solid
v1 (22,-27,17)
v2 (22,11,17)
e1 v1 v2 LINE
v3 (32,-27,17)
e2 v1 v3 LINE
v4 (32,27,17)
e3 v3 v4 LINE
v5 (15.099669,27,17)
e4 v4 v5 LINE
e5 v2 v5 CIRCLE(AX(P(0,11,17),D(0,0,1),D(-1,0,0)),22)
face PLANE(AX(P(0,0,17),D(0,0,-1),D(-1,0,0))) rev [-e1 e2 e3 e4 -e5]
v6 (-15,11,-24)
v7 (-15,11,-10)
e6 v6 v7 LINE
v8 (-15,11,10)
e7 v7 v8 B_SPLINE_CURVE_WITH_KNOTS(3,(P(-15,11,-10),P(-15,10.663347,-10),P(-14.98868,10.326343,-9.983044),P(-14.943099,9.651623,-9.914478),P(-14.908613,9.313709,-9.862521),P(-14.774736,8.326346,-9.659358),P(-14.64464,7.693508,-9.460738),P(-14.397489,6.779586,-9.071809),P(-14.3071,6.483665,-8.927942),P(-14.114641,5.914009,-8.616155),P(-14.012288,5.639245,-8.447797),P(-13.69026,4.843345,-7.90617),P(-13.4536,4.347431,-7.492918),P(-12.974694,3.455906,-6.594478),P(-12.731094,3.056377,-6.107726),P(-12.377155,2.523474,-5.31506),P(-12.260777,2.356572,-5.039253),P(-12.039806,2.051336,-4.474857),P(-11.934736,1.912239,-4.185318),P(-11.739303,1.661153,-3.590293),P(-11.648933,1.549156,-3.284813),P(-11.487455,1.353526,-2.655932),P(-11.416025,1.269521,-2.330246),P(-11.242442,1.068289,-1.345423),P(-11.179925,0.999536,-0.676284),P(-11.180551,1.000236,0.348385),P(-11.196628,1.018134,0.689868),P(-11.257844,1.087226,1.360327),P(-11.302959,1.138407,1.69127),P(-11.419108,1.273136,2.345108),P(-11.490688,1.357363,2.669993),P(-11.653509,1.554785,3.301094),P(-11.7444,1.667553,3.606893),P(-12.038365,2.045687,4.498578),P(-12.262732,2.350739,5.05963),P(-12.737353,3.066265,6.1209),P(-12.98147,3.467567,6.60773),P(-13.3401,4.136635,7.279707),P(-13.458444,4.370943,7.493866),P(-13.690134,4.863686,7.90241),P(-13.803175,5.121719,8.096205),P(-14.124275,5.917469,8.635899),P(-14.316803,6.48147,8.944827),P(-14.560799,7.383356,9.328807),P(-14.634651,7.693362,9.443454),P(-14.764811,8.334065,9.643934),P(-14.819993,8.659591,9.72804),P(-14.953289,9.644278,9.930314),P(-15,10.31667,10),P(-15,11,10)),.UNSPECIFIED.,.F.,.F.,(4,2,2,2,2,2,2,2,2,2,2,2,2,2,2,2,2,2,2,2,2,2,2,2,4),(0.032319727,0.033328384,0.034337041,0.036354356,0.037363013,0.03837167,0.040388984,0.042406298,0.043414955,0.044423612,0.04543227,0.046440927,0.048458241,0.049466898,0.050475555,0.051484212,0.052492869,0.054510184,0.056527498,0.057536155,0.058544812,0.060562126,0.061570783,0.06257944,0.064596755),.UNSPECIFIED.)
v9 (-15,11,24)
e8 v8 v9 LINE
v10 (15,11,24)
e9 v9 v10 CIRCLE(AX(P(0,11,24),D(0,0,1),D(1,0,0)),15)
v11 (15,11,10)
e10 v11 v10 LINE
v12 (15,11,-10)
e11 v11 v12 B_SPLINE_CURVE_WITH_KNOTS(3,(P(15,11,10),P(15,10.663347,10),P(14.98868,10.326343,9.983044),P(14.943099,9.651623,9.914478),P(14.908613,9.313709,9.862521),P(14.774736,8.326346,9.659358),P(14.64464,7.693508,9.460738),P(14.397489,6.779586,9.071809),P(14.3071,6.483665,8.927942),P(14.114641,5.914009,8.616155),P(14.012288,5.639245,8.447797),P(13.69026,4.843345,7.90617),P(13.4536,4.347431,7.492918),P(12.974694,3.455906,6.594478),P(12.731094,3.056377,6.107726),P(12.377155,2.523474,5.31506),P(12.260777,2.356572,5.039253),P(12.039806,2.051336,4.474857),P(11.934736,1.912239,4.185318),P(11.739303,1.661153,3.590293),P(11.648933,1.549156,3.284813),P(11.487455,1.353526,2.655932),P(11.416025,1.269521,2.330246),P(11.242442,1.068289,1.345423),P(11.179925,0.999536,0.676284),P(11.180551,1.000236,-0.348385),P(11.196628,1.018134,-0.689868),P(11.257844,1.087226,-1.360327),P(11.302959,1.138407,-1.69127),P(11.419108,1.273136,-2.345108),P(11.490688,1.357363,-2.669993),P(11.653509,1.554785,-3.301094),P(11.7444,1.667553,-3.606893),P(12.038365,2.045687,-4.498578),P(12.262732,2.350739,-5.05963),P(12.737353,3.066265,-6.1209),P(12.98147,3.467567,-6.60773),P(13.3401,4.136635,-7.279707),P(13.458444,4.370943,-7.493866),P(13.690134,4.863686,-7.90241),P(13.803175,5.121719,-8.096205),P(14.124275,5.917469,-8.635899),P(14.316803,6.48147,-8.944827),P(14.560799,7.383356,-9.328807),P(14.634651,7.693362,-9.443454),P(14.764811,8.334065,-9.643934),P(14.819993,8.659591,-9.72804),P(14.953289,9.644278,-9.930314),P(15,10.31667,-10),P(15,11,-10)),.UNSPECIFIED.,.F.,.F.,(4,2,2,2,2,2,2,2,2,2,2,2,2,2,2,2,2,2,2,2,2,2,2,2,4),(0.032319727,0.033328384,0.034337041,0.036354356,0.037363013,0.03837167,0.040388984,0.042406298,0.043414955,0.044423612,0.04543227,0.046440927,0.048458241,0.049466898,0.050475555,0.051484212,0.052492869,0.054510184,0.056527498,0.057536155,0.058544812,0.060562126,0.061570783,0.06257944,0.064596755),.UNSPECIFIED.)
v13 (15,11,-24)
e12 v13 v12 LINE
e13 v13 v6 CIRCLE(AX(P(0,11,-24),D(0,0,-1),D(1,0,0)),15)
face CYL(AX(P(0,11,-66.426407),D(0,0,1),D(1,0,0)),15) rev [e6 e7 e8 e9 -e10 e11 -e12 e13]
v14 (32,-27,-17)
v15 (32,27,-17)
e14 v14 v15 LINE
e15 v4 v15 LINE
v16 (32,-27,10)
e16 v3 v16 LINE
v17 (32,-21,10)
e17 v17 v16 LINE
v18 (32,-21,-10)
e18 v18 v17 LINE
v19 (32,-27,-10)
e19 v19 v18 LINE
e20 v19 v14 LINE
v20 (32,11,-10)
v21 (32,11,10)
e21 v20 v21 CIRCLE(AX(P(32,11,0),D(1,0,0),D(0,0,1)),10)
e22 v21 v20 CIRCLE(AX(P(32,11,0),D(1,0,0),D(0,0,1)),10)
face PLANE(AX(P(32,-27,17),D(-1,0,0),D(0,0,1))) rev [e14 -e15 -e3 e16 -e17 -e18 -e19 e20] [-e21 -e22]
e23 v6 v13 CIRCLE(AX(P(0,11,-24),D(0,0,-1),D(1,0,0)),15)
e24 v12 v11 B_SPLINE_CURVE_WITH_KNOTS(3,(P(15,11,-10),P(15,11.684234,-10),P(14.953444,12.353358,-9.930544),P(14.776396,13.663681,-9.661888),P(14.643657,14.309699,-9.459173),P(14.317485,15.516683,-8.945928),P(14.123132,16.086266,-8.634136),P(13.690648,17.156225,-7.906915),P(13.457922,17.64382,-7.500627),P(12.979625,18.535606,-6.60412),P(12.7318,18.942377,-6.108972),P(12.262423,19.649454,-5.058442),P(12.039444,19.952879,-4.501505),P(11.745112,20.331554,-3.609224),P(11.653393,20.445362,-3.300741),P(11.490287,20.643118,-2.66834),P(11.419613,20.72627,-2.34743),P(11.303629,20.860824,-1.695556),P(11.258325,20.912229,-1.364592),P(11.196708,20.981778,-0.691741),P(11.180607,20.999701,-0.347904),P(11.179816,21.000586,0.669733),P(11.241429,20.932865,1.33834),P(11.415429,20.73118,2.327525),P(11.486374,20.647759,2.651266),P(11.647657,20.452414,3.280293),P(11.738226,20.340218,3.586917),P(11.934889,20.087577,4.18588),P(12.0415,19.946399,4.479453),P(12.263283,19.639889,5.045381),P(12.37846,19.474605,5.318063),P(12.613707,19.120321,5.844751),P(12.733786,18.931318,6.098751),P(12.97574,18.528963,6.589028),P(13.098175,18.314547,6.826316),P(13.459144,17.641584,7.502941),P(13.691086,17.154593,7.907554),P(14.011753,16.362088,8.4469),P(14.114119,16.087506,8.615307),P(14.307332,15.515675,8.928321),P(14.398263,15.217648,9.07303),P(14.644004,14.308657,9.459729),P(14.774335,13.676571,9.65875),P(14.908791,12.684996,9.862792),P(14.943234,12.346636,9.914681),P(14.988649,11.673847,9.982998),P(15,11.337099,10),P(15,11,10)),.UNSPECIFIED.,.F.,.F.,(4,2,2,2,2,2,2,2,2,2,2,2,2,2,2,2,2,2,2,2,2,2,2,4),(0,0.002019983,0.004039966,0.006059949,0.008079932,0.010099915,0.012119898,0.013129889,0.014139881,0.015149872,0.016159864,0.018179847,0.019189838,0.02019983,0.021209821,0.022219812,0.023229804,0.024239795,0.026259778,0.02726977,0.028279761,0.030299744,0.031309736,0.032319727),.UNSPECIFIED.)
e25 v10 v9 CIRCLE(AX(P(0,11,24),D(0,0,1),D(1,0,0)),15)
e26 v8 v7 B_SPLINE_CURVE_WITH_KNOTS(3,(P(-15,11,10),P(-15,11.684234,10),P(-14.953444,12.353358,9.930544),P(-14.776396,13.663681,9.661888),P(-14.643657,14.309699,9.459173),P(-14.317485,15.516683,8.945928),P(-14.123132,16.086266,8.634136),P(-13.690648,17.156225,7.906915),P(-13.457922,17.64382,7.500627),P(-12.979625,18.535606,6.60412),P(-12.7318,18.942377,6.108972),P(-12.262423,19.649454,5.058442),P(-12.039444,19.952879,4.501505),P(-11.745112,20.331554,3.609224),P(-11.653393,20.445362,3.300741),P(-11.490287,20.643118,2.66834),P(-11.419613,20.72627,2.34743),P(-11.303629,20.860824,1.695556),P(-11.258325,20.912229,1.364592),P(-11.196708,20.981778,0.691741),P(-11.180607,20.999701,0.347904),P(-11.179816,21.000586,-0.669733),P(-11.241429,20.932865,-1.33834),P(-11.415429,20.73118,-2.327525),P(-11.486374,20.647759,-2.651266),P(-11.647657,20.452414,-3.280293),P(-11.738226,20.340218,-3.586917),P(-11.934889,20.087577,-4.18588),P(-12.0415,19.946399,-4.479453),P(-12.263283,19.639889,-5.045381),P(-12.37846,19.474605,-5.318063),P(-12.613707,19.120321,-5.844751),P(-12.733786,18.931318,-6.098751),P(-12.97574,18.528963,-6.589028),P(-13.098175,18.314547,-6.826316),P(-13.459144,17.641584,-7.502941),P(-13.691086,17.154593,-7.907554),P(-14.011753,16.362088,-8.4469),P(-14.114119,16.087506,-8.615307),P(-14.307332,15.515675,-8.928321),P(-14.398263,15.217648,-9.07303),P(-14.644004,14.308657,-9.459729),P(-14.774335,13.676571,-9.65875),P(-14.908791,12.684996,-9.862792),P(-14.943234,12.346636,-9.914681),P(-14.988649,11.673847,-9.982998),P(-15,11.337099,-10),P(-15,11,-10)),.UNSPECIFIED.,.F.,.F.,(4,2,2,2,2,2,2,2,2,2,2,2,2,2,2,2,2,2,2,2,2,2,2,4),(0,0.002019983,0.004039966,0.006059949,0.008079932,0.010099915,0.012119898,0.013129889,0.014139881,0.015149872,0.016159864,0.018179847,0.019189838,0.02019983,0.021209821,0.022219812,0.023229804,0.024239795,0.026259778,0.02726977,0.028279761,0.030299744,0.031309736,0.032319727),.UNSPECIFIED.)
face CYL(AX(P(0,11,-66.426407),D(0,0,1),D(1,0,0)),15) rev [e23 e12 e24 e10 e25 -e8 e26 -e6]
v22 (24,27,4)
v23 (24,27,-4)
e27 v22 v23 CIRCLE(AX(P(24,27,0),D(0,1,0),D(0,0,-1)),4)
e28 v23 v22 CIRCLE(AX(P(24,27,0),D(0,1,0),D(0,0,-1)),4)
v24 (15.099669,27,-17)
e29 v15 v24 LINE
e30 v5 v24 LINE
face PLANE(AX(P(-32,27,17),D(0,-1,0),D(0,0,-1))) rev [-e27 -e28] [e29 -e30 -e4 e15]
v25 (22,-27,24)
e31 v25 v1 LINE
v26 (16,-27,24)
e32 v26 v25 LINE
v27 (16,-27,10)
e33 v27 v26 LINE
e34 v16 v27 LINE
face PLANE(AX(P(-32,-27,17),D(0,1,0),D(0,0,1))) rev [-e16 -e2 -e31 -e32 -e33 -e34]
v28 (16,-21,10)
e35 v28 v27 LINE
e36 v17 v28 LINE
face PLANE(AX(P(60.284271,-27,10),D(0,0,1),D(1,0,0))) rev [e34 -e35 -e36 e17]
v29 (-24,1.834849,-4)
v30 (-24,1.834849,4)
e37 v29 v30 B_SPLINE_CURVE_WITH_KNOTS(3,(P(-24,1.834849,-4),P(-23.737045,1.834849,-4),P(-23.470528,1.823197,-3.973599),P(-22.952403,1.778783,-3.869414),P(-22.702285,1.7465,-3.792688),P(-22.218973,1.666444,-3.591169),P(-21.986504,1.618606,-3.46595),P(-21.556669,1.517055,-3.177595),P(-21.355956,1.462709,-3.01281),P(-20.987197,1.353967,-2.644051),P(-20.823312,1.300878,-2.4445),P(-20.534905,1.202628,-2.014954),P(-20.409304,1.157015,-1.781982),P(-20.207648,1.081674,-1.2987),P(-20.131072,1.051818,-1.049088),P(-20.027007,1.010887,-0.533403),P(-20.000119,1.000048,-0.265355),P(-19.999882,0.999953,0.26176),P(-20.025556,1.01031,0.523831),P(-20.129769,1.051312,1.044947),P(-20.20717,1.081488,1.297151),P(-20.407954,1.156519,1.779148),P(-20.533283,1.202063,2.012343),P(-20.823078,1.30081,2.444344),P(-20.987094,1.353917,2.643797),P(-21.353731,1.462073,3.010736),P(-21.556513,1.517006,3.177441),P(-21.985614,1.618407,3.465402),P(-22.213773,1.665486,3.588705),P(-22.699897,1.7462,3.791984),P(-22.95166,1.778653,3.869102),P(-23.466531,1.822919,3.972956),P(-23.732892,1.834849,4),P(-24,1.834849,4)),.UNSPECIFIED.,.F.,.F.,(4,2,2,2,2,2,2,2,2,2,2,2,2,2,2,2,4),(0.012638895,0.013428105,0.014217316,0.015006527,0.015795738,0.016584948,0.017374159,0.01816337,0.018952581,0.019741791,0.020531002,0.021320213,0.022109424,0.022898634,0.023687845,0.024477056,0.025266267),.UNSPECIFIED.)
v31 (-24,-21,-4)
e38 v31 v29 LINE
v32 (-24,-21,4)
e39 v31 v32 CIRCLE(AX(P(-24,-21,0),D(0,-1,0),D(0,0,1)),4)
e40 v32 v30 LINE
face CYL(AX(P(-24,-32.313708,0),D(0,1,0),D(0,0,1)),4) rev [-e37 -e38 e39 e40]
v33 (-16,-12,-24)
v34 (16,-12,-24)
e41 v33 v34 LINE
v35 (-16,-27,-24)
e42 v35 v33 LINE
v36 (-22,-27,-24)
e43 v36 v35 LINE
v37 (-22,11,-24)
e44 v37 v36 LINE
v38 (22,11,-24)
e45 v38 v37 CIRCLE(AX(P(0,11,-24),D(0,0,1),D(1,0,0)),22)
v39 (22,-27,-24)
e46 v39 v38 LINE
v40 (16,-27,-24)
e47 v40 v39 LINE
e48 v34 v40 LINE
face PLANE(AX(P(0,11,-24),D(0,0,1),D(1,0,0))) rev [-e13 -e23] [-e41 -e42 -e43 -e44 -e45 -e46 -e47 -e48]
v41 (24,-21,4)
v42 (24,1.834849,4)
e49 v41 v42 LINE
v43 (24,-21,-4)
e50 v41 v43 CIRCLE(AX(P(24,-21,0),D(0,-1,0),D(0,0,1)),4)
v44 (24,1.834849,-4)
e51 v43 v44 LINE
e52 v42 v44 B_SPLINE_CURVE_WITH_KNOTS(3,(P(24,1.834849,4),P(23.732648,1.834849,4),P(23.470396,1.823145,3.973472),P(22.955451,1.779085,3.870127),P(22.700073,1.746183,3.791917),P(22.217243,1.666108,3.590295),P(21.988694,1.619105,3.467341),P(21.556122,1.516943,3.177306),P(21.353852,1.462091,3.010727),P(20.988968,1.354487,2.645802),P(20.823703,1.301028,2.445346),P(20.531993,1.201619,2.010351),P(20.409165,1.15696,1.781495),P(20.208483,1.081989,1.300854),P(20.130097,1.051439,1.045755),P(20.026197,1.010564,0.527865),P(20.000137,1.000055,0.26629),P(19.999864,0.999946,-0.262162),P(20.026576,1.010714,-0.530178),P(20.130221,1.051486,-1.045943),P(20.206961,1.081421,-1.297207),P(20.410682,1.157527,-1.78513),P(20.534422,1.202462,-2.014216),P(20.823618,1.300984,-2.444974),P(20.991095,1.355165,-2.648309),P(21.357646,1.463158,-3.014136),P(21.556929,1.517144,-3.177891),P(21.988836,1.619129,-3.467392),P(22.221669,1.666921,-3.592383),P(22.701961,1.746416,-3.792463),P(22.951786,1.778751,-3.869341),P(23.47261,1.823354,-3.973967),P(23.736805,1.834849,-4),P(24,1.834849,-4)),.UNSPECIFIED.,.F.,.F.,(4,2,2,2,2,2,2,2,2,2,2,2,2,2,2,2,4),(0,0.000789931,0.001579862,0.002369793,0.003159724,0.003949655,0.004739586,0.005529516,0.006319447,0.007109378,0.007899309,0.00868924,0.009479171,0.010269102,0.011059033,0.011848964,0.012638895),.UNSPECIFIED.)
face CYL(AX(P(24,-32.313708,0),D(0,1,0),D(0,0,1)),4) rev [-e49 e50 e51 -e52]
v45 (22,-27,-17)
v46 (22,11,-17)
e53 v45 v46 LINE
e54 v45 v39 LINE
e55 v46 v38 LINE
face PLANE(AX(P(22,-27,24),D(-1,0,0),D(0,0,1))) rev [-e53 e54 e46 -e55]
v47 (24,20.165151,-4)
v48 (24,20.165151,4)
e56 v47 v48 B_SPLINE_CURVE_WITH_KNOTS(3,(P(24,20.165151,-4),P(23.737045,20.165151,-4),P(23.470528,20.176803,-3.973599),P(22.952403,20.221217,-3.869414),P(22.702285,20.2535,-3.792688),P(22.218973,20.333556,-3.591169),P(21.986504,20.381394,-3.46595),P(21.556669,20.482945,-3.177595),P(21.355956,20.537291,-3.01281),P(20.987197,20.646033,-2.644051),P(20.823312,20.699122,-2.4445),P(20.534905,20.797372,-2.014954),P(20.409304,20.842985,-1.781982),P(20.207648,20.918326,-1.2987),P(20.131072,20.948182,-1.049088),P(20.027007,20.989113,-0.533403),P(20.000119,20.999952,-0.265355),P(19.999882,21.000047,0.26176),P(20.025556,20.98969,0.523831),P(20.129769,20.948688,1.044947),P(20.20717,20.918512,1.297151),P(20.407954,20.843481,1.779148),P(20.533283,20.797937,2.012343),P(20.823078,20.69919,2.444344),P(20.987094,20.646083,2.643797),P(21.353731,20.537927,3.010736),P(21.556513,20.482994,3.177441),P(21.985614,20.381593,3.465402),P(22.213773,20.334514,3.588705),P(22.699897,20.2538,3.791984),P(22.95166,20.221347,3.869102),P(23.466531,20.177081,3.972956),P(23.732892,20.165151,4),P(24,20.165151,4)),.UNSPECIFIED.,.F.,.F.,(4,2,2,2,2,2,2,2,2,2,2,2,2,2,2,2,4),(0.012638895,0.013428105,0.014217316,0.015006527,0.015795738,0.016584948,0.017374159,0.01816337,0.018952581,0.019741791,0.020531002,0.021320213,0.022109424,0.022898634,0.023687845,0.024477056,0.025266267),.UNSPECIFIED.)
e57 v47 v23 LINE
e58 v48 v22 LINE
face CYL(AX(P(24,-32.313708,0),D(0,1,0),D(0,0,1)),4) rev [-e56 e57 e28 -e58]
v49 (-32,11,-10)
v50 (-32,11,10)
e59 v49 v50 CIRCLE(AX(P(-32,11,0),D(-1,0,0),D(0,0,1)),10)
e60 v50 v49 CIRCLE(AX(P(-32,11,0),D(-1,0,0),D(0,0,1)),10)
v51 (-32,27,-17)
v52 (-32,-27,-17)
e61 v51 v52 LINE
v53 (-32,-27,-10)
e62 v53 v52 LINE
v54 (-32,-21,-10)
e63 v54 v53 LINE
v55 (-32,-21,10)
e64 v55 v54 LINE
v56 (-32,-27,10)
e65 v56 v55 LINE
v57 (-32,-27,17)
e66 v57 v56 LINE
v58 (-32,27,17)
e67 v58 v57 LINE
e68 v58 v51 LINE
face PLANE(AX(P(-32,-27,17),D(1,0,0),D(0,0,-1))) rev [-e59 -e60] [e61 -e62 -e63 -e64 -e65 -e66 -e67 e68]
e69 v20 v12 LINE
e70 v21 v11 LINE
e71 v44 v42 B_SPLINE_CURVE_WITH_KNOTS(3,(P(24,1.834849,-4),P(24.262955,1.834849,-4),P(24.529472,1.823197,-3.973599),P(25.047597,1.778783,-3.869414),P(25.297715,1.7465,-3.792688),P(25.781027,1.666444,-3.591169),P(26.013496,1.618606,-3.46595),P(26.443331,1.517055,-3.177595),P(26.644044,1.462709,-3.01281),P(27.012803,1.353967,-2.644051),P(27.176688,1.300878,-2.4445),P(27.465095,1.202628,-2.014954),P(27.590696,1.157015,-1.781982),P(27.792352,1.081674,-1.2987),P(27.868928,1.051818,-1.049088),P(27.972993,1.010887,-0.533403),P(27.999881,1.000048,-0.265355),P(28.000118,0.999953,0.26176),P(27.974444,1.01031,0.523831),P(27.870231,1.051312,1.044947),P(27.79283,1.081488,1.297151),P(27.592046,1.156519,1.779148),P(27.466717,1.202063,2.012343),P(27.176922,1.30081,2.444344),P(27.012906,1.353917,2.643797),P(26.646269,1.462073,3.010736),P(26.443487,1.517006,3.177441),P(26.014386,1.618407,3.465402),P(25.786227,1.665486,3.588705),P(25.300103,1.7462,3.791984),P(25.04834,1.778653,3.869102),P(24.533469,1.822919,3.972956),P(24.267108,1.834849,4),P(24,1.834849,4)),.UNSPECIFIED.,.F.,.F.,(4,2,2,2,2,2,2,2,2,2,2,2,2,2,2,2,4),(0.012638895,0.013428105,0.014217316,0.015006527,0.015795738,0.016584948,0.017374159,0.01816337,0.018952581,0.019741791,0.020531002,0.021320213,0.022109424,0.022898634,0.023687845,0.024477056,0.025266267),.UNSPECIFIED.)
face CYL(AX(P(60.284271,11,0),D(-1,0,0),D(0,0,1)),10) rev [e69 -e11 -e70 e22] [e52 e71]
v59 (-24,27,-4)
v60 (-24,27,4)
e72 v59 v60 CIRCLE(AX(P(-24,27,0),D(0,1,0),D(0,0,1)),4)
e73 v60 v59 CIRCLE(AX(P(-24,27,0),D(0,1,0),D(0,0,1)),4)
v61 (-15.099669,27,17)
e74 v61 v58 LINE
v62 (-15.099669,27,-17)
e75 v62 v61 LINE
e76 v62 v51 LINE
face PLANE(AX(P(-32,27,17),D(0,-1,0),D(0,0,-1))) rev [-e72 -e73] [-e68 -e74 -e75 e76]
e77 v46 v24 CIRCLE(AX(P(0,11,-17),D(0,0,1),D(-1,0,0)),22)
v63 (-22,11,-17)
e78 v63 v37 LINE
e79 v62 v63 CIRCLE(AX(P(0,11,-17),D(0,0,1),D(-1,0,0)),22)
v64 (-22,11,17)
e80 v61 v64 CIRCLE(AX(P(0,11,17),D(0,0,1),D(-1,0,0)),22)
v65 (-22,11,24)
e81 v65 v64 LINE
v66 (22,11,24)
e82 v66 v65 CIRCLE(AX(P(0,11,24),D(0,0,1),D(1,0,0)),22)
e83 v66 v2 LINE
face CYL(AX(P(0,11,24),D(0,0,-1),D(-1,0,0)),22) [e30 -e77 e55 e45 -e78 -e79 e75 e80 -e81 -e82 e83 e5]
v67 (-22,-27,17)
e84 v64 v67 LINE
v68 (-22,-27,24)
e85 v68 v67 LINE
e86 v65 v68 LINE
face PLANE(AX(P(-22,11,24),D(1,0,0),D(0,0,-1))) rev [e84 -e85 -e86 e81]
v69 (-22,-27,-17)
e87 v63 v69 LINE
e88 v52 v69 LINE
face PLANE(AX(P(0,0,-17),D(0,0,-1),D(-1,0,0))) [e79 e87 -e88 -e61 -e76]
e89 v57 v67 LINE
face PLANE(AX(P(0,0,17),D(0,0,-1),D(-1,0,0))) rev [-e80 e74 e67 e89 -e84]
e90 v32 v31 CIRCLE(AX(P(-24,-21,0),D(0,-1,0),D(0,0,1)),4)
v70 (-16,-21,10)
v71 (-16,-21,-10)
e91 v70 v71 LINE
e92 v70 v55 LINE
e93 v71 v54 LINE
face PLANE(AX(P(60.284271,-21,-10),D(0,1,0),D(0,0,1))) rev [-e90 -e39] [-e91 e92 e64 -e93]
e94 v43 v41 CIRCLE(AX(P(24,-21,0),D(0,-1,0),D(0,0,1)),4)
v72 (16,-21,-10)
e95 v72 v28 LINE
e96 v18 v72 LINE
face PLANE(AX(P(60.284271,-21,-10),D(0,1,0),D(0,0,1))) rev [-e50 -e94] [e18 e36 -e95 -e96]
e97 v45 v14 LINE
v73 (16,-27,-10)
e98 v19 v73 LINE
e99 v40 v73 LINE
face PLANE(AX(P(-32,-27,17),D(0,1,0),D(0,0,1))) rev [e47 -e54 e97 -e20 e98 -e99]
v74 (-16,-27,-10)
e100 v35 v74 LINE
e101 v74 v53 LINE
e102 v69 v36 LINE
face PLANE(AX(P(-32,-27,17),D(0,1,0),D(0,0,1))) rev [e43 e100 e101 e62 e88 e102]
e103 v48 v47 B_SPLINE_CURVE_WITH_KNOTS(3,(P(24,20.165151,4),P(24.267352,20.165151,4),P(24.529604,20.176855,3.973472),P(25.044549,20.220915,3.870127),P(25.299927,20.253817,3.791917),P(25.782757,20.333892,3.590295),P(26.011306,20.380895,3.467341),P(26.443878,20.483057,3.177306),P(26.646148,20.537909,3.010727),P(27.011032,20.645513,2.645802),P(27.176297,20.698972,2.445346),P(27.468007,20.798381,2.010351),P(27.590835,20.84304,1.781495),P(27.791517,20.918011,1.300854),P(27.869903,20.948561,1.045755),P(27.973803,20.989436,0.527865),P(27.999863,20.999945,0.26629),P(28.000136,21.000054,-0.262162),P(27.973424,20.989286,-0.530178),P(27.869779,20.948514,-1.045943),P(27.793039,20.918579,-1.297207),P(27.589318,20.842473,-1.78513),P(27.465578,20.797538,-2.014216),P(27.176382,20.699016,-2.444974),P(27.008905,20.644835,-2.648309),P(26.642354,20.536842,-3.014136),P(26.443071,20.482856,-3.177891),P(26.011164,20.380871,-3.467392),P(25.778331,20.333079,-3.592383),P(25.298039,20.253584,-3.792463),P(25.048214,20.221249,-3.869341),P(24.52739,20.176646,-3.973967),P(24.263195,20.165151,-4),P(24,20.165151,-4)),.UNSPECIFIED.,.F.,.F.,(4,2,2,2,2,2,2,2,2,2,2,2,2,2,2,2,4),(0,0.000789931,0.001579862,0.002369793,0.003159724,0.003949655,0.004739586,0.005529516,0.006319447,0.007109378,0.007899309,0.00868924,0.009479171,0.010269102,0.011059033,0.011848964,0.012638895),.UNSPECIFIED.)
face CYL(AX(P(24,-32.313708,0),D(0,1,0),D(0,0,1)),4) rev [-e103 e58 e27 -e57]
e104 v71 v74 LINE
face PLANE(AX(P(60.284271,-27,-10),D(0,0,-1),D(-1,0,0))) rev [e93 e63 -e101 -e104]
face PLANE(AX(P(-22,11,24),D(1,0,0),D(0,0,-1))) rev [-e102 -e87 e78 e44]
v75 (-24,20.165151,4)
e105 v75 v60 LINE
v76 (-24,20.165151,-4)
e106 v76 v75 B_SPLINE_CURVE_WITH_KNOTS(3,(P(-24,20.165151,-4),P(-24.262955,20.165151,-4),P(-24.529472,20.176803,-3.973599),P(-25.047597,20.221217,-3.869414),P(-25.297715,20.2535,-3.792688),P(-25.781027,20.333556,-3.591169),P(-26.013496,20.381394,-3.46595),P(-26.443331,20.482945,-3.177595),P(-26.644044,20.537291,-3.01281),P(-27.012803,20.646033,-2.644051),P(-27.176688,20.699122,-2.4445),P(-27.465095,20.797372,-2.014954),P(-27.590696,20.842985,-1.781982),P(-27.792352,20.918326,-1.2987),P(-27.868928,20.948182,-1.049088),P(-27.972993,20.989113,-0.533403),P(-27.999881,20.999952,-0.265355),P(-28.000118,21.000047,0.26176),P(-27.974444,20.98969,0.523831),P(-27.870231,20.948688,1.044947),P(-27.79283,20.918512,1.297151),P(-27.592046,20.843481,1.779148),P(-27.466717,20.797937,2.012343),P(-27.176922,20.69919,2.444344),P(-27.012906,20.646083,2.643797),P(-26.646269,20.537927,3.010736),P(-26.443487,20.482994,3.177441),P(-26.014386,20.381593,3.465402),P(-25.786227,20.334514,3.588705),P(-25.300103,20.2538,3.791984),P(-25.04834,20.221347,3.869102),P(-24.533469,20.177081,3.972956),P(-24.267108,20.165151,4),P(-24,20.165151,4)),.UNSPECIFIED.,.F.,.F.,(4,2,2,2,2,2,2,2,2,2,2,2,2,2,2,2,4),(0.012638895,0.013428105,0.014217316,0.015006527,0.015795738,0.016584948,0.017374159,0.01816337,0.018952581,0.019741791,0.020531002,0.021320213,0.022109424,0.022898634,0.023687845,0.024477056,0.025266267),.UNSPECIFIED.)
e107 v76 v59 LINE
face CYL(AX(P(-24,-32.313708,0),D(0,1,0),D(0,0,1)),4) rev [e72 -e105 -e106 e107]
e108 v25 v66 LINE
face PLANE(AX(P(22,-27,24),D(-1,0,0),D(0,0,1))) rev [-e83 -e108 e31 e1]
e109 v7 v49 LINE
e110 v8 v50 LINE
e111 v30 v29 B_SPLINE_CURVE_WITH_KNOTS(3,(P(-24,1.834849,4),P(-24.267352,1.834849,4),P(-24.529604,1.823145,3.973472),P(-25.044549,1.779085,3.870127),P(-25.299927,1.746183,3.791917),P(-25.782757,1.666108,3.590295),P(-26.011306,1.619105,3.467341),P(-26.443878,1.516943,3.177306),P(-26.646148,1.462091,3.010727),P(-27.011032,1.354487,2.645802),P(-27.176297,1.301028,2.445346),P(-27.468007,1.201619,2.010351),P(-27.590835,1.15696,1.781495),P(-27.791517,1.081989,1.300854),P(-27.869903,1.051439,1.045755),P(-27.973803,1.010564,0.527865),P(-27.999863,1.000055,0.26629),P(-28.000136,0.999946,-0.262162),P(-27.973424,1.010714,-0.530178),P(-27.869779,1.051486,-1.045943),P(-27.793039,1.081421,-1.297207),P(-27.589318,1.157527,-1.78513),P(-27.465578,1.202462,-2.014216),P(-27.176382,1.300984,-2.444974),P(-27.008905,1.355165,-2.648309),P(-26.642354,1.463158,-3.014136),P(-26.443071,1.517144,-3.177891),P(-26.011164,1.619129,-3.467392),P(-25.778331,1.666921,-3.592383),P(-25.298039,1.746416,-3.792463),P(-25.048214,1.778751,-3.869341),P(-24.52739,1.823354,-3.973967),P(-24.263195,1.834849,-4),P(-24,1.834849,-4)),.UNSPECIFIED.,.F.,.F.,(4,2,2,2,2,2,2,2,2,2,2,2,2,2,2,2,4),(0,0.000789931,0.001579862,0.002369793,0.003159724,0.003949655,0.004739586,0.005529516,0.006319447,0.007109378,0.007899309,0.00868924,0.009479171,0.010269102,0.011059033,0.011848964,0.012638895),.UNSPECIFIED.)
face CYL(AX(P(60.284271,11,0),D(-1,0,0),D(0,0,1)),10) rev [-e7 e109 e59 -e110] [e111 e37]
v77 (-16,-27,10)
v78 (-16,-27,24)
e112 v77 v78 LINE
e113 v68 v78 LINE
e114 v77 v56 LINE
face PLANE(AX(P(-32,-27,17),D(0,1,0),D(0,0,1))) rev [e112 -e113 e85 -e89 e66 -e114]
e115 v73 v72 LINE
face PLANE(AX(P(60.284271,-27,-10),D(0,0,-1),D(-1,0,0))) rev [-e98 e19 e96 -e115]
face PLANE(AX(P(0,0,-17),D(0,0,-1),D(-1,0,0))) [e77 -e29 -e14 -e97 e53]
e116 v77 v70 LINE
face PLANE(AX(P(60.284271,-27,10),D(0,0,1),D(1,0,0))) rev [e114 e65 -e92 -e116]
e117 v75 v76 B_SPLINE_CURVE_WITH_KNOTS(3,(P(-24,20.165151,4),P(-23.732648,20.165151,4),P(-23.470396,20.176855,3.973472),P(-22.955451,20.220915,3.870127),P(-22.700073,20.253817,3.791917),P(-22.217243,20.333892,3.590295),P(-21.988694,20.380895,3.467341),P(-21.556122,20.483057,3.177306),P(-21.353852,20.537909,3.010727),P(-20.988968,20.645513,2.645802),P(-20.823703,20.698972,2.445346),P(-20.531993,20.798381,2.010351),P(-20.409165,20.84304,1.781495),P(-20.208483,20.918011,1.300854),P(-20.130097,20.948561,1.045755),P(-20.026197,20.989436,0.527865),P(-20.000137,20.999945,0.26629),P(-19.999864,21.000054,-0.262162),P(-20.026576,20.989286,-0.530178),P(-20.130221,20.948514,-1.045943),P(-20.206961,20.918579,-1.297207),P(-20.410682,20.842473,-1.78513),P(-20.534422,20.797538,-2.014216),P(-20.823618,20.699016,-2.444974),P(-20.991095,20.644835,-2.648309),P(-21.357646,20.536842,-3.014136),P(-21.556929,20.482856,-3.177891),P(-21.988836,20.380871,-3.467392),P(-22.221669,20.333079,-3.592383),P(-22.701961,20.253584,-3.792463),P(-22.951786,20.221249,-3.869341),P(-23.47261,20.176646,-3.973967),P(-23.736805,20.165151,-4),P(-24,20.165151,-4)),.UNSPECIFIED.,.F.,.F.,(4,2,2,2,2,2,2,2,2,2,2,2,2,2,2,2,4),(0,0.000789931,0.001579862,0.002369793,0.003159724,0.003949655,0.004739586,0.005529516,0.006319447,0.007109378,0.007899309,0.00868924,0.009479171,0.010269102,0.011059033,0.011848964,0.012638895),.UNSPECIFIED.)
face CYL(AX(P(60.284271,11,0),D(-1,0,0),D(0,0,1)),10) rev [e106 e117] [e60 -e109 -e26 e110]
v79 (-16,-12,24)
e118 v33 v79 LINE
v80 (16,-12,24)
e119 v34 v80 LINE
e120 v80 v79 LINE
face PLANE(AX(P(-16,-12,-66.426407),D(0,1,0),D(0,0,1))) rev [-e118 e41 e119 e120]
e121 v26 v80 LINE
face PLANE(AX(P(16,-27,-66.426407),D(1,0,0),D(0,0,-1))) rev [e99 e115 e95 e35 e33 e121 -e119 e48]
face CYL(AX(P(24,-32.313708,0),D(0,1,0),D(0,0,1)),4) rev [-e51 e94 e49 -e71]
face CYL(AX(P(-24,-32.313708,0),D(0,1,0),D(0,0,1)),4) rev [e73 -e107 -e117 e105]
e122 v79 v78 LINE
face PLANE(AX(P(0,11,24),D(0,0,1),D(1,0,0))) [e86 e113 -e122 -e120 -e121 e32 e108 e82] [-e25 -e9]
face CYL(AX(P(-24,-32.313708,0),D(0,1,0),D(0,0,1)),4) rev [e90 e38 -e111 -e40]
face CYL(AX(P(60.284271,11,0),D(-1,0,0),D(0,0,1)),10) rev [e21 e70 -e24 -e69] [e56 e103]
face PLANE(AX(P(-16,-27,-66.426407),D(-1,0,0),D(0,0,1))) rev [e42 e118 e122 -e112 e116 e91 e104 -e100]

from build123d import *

# Parameters (mm, degrees)
BASE_BLOCK_PROFILE_W       = 64
BASE_BLOCK_PROFILE_H       = 54
BASE_BLOCK_DEPTH           = 17
BEARING_HOUSING_BOSS_DEPTH = 24
MAIN_BORE_PROFILE_R        = 15
MAIN_BORE_PROFILE_W        = 32
MAIN_BORE_PROFILE_H        = 15
MAIN_BORE_DEPTH            = 48
CROSS_HOLES_REACH          = 77.901
CROSS_HOLE_PROFILE_R       = 10
CROSS_HOLE_PROFILE_W       = 20
CROSS_HOLE_PROFILE_H       = 6
TOP_PIN_HOLES_REACH        = 69.201
TOP_PIN_HOLE_PROFILE_R     = 4


with BuildPart() as part:
    # Base Block Profile → Base Block (new, symmetric)
    with BuildSketch(Plane.XY):
        Rectangle(BASE_BLOCK_PROFILE_W, BASE_BLOCK_PROFILE_H)
    extrude(amount=BASE_BLOCK_DEPTH, both=True)

    # Housing Boss Profile → Bearing Housing Boss (add, symmetric)
    with BuildSketch(Plane.XY):
        with BuildLine():
            Line((-22, 11), (-22, -27))
            Line((-22, -27), (22, -27))
            Line((22, -27), (22, 11))
            ThreePointArc((22, 11), (0, 33), (-22, 11))
        make_face()
    extrude(amount=BEARING_HOUSING_BOSS_DEPTH, both=True)

    # Main Bore Profile → Main Bore (cut)
    with BuildSketch(Plane.XY.offset(24)):
        with Locations((0, 11)):
            Circle(MAIN_BORE_PROFILE_R)
        with Locations((0, -19.5)):
            Rectangle(MAIN_BORE_PROFILE_W, MAIN_BORE_PROFILE_H)
    extrude(amount=-MAIN_BORE_DEPTH, mode=Mode.SUBTRACT)

    # Cross Holes: up to this face of the body (flat: up to its plane)
    cross_holes_end = Plane(part.part.faces().sort_by_distance((32, 0, 0))[0])
    # Cross Hole Profile → Cross Holes (cut, up to the picked face)
    with BuildSketch(Plane.ZY.offset(32), mode=Mode.PRIVATE) as cross_holes_sk1:
        with Locations((0, 11)):
            Circle(CROSS_HOLE_PROFILE_R)
    cross_holes_tool1 = split(extrude(cross_holes_sk1.sketch, amount=-CROSS_HOLES_REACH, mode=Mode.PRIVATE), bisect_by=cross_holes_end, keep=Keep.BOTH, mode=Mode.PRIVATE)
    # Cross Hole Profile → Cross Holes (cut, up to the picked face)
    with BuildSketch(Plane.ZY.offset(32), mode=Mode.PRIVATE) as cross_holes_sk2:
        with Locations((0, -24)):
            Rectangle(CROSS_HOLE_PROFILE_W, CROSS_HOLE_PROFILE_H)
    cross_holes_tool2 = split(extrude(cross_holes_sk2.sketch, amount=-CROSS_HOLES_REACH, mode=Mode.PRIVATE), bisect_by=cross_holes_end, keep=Keep.BOTH, mode=Mode.PRIVATE)
    add(cross_holes_tool1.solids().sort_by(Axis((-32, 11, 0), (1, 0, 0)))[0], mode=Mode.SUBTRACT)
    add(cross_holes_tool2.solids().sort_by(Axis((-32, -24, 0), (1, 0, 0)))[0], mode=Mode.SUBTRACT)

    # Top Pin Holes: up to this face of the body (flat: up to its plane)
    top_pin_holes_end = Plane(part.part.faces().sort_by_distance((-24, -21, 0))[0])
    # Top Pin Hole Profile → Top Pin Holes (cut, up to the picked face)
    with BuildSketch(Plane(origin=(0, 27, 0), x_dir=(1, 0, 0), z_dir=(0, 1, 0)), mode=Mode.PRIVATE) as top_pin_holes_sk1:
        with Locations(Location((-24, 0, 0), (0, 0, 270))):
            Circle(TOP_PIN_HOLE_PROFILE_R)
    top_pin_holes_tool1 = split(extrude(top_pin_holes_sk1.sketch, amount=-TOP_PIN_HOLES_REACH, mode=Mode.PRIVATE), bisect_by=top_pin_holes_end, keep=Keep.BOTH, mode=Mode.PRIVATE)
    # Top Pin Hole Profile → Top Pin Holes (cut, up to the picked face)
    with BuildSketch(Plane(origin=(0, 27, 0), x_dir=(1, 0, 0), z_dir=(0, 1, 0)), mode=Mode.PRIVATE) as top_pin_holes_sk2:
        with Locations(Location((24, 0, 0), (0, 0, 270))):
            Circle(TOP_PIN_HOLE_PROFILE_R)
    top_pin_holes_tool2 = split(extrude(top_pin_holes_sk2.sketch, amount=-TOP_PIN_HOLES_REACH, mode=Mode.PRIVATE), bisect_by=top_pin_holes_end, keep=Keep.BOTH, mode=Mode.PRIVATE)
    add(top_pin_holes_tool1.solids().sort_by(Axis((-24, 27, 0), (0, -1, 0)))[0], mode=Mode.SUBTRACT)
    add(top_pin_holes_tool2.solids().sort_by(Axis((24, 27, 0), (0, -1, 0)))[0], mode=Mode.SUBTRACT)


solid = part.part
